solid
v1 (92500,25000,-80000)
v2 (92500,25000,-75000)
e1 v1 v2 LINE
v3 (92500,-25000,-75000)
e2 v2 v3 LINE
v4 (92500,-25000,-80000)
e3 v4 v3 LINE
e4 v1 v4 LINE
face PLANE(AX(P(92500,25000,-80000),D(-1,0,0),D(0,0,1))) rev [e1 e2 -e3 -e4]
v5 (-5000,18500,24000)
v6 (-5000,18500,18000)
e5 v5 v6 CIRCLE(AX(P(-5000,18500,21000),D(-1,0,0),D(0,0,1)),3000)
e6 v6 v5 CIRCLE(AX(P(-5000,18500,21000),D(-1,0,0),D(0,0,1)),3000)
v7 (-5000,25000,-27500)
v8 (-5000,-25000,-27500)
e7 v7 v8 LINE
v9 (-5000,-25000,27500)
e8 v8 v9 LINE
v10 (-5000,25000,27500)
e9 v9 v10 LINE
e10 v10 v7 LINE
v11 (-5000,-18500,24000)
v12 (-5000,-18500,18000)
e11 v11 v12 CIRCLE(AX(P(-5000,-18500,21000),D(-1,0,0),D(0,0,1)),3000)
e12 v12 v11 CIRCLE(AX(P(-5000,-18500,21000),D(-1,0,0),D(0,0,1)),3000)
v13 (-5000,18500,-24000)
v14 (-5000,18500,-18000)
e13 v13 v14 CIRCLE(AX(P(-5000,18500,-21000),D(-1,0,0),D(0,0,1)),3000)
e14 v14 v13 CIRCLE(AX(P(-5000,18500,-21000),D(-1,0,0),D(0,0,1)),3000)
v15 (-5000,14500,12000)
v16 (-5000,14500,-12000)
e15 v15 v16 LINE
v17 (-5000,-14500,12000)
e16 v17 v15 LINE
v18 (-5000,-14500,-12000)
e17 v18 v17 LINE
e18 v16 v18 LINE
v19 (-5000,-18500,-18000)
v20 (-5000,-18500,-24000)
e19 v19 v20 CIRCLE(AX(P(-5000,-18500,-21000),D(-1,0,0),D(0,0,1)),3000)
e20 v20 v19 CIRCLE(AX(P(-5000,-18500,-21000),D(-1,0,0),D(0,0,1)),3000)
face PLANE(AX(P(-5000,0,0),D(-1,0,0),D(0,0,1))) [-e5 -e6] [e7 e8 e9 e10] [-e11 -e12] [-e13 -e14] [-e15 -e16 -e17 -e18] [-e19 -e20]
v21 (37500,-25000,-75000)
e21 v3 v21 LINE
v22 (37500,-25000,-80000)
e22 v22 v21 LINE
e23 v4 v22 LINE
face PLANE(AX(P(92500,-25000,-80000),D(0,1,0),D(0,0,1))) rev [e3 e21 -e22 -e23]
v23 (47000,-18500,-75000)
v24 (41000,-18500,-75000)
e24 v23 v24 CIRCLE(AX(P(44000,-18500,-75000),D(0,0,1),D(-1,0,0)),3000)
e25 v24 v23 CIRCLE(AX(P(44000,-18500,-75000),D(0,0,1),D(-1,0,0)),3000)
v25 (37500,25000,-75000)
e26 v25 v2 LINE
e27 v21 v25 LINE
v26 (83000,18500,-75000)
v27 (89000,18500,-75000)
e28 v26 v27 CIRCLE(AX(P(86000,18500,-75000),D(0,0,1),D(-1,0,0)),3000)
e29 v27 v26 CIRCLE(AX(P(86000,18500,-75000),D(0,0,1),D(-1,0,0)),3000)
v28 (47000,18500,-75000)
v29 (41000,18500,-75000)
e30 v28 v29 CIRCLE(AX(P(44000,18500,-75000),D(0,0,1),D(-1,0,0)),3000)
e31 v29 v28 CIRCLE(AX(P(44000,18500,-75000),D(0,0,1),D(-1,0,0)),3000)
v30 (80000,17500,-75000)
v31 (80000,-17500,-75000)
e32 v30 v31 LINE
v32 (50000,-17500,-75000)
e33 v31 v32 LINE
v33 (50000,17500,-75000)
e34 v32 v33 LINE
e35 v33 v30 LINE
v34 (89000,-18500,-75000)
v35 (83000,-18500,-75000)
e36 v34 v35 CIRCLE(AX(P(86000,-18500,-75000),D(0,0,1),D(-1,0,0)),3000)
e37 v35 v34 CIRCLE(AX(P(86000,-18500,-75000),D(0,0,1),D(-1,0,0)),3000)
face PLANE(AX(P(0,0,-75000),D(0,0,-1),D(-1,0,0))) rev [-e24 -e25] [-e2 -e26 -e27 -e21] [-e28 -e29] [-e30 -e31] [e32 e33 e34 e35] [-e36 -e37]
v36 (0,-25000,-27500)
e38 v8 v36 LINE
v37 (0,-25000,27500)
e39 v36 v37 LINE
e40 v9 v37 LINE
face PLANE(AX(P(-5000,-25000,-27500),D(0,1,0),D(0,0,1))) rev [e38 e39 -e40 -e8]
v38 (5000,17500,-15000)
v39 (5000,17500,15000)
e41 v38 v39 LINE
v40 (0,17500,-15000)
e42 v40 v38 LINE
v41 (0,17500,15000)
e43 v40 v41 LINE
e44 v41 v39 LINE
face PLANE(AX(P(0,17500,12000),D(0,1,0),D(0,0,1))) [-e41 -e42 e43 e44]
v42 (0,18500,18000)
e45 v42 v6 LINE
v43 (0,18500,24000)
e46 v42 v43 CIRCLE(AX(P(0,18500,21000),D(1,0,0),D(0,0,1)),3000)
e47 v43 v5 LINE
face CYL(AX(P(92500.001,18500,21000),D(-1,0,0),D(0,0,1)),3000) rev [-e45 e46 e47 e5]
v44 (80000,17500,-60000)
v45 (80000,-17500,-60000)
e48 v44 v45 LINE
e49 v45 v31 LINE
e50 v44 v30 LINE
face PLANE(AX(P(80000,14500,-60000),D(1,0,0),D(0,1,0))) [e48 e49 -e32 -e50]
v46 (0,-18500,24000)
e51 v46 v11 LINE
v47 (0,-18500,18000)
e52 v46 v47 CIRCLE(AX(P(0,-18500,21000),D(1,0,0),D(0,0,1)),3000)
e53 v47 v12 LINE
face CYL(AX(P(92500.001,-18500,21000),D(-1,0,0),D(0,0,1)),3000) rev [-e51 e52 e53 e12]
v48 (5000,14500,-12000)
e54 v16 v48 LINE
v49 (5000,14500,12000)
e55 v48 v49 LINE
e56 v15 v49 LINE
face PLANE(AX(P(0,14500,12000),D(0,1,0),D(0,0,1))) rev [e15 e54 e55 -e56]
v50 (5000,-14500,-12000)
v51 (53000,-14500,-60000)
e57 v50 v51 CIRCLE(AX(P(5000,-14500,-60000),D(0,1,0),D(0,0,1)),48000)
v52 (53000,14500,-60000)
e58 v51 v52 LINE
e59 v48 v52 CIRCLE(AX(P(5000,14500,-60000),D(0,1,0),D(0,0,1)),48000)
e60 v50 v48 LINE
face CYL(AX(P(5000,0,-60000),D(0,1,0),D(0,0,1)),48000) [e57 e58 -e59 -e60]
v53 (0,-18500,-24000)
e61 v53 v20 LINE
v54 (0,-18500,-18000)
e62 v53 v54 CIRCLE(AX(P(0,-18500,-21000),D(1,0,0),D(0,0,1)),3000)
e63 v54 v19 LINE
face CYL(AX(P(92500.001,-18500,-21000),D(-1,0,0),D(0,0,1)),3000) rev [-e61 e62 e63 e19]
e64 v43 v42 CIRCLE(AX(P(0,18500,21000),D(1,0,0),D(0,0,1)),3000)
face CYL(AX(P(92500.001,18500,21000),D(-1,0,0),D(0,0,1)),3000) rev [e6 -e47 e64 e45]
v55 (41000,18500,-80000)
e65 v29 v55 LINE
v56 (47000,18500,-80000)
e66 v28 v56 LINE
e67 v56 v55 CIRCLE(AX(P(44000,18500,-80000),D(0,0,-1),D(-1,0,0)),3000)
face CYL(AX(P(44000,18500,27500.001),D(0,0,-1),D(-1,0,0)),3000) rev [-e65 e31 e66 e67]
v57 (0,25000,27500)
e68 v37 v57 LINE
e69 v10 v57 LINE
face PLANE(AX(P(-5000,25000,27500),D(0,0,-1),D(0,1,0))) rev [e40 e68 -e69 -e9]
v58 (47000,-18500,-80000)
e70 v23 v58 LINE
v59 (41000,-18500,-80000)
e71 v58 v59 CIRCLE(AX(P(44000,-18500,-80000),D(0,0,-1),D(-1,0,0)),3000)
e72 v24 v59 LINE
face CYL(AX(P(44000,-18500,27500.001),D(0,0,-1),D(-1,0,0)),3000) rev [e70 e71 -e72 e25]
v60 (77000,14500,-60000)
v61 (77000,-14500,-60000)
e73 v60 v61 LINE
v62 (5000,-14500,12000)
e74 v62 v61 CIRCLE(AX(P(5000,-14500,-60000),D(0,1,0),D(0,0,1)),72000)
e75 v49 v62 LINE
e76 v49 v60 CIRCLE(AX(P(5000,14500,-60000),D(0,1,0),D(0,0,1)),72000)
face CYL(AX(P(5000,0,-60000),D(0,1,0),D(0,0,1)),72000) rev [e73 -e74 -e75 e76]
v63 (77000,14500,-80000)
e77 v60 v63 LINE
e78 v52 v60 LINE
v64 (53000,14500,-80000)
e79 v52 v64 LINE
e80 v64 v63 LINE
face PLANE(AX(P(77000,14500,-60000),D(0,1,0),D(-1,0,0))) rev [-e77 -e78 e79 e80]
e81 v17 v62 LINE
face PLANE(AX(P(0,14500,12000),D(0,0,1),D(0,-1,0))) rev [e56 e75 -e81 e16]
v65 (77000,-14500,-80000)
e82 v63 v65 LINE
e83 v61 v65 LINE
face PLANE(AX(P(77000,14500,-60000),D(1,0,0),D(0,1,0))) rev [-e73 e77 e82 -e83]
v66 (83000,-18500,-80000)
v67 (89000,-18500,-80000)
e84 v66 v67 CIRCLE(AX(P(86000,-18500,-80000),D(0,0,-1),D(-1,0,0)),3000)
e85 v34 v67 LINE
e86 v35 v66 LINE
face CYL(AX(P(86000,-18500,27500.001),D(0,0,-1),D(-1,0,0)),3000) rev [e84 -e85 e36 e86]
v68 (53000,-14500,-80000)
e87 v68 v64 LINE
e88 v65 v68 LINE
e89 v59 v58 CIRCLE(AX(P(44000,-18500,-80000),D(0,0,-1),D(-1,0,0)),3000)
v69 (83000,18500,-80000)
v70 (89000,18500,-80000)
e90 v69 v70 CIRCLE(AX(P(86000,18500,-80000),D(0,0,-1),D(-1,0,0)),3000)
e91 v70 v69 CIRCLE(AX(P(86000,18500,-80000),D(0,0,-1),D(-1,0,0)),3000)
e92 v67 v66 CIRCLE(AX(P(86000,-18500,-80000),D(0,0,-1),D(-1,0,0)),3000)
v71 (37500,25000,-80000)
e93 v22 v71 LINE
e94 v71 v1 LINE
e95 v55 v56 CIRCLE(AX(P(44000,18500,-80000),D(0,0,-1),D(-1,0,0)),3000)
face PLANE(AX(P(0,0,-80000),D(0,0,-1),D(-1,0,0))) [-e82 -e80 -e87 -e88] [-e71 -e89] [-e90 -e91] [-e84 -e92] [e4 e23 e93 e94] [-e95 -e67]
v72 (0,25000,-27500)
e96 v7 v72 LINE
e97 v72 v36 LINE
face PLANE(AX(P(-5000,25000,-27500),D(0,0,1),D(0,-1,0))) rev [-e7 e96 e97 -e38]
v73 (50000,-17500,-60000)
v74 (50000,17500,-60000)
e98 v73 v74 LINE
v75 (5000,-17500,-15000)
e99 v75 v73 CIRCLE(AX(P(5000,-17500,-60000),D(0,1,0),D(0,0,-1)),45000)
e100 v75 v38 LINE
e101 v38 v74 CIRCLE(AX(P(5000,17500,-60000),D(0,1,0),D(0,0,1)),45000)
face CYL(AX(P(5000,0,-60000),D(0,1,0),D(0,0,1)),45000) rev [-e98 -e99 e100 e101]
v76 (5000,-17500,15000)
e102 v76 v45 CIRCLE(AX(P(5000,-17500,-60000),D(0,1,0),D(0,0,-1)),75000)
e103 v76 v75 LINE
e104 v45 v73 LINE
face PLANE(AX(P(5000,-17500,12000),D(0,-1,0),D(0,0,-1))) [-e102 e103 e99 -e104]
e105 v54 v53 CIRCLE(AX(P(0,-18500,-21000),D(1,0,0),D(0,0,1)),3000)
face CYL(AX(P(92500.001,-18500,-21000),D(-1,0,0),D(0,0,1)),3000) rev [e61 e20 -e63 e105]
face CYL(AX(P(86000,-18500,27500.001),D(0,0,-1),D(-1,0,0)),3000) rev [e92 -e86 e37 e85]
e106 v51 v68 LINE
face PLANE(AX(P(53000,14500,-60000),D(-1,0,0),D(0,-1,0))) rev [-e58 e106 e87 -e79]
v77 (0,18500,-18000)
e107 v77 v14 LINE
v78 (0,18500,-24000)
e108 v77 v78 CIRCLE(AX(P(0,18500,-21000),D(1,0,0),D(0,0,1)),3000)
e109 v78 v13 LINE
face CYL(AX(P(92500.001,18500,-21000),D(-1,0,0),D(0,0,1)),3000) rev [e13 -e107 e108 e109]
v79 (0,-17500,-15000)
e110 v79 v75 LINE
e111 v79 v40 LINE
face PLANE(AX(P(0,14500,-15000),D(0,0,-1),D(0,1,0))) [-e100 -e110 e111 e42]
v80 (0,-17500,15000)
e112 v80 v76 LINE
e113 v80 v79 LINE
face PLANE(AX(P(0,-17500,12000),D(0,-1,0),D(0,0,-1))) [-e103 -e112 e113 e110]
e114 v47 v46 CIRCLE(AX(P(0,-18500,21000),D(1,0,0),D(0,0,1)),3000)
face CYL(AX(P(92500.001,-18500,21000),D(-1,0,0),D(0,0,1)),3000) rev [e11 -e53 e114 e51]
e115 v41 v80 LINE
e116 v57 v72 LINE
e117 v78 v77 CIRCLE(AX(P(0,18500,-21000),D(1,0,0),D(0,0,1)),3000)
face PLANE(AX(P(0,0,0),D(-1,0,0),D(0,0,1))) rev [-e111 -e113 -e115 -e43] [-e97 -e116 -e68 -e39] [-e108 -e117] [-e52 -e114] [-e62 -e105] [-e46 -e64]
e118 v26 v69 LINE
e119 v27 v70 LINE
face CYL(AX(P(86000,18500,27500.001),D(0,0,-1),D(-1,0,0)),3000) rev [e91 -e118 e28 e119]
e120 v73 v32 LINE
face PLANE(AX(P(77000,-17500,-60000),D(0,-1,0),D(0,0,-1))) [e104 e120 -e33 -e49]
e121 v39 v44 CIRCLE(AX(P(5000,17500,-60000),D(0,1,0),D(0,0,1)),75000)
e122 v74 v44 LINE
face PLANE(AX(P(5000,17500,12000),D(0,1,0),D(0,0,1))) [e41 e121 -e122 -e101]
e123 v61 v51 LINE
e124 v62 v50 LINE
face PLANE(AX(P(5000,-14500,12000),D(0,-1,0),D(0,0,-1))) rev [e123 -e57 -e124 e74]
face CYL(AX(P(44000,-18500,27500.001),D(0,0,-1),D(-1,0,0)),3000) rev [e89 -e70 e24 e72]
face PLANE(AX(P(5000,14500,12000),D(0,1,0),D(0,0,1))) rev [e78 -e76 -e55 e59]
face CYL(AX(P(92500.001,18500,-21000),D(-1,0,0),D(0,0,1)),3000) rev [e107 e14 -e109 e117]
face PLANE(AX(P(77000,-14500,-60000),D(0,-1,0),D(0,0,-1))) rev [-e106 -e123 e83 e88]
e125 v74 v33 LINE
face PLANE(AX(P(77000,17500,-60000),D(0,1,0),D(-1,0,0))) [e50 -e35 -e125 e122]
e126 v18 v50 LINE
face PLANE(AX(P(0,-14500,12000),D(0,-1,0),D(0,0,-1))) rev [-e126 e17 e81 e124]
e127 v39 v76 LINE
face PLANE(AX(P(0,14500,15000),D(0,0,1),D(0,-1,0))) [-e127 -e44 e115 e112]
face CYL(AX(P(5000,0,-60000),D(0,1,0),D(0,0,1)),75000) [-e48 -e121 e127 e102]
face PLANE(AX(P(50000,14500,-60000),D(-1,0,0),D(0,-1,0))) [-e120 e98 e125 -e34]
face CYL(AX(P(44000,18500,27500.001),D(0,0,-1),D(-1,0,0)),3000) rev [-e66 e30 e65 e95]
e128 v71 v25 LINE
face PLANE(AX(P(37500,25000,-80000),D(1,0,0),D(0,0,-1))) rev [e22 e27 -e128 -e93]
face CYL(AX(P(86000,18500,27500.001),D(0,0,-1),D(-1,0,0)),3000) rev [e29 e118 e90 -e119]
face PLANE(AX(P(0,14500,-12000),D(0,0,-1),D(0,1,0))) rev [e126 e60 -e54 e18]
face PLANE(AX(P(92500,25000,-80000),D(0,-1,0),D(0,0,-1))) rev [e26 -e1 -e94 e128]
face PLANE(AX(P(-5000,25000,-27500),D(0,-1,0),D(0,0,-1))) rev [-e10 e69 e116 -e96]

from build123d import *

# Parameters (mm, degrees)
DUCT_PROFILE_SKETCH_W        = 30000
DUCT_PROFILE_SKETCH_H        = 35000
DUCT_PROFILE_SKETCH_W_2      = 24000
DUCT_PROFILE_SKETCH_H_2      = 29000
FLANGE_A_SKETCH_W            = 55000
FLANGE_A_SKETCH_H            = 50000
FLANGE_A_SKETCH_W_2          = 24000
FLANGE_A_SKETCH_H_2          = 29000
FLANGE_A_DEPTH               = 5000
FLANGE_B_SKETCH_W            = 55000
FLANGE_B_SKETCH_H            = 50000
FLANGE_B_SKETCH_W_2          = 24000
FLANGE_B_SKETCH_H_2          = 29000
FLANGE_B_DEPTH               = 5000
FLANGE_B_BOLT_HOLES_4X_REACH = 144007.208
FLANGE_B_BOLT_HOLES_SKETCH_R = 3000
FLANGE_A_BOLT_HOLES_4X_REACH = 128575.909
FLANGE_A_BOLT_HOLES_SKETCH_R = 3000


with BuildPart() as part:
    # Duct Elbow Thin Sweep: sweep along a path in Elbow Path Sketch
    with BuildLine(Plane(origin=(0, 0, 0), x_dir=(1, 0, 0), z_dir=(0, 1, 0))) as duct_elbow_thin_sweep_path:
        Line((0, 0), (5000, 0))
        ThreePointArc((5000, 0), (47426.406871193, 17573.593128807), (65000, 60000))
        Line((65000, 60000), (65000, 75000))
    # Duct Profile Sketch → Duct Elbow Thin Sweep (sweep)
    with BuildSketch(Plane(origin=(0, 0, 0), x_dir=(0, 0, -1), z_dir=(1, 0, 0))):
        Rectangle(DUCT_PROFILE_SKETCH_W, DUCT_PROFILE_SKETCH_H)
        Rectangle(DUCT_PROFILE_SKETCH_W_2, DUCT_PROFILE_SKETCH_H_2, mode=Mode.SUBTRACT)
    sweep(path=duct_elbow_thin_sweep_path.line)

    # Flange A Sketch → Flange A (add)
    with BuildSketch(Plane.ZY):
        Rectangle(FLANGE_A_SKETCH_W, FLANGE_A_SKETCH_H)
        Rectangle(FLANGE_A_SKETCH_W_2, FLANGE_A_SKETCH_H_2, mode=Mode.SUBTRACT)
    extrude(amount=FLANGE_A_DEPTH)

    # Flange B Sketch → Flange B (add)
    with BuildSketch(Plane(origin=(0, 0, -75000), x_dir=(-1, 0, 0), z_dir=(0, 0, -1))):
        with Locations((-65000, 0)):
            Rectangle(FLANGE_B_SKETCH_W, FLANGE_B_SKETCH_H)
        with Locations((-65000, 0)):
            Rectangle(FLANGE_B_SKETCH_W_2, FLANGE_B_SKETCH_H_2, mode=Mode.SUBTRACT)
    extrude(amount=FLANGE_B_DEPTH)

    # Flange B Bolt Holes Sketch → Flange B Bolt Holes 4x (cut, up to next)
    with BuildSketch(Plane(origin=(0, 0, -80000), x_dir=(-1, 0, 0), z_dir=(0, 0, -1)), mode=Mode.PRIVATE) as flange_b_bolt_holes_4x_sk1:
        with Locations((-86000, 18500)):
            Circle(FLANGE_B_BOLT_HOLES_SKETCH_R)
    flange_b_bolt_holes_4x_tool1 = extrude(flange_b_bolt_holes_4x_sk1.sketch, amount=-FLANGE_B_BOLT_HOLES_4X_REACH, mode=Mode.PRIVATE) & part.part
    # Flange B Bolt Holes Sketch → Flange B Bolt Holes 4x (cut, up to next)
    with BuildSketch(Plane(origin=(0, 0, -80000), x_dir=(-1, 0, 0), z_dir=(0, 0, -1)), mode=Mode.PRIVATE) as flange_b_bolt_holes_4x_sk2:
        with Locations((-44000, 18500)):
            Circle(FLANGE_B_BOLT_HOLES_SKETCH_R)
    flange_b_bolt_holes_4x_tool2 = extrude(flange_b_bolt_holes_4x_sk2.sketch, amount=-FLANGE_B_BOLT_HOLES_4X_REACH, mode=Mode.PRIVATE) & part.part
    # Flange B Bolt Holes Sketch → Flange B Bolt Holes 4x (cut, up to next)
    with BuildSketch(Plane(origin=(0, 0, -80000), x_dir=(-1, 0, 0), z_dir=(0, 0, -1)), mode=Mode.PRIVATE) as flange_b_bolt_holes_4x_sk3:
        with Locations((-44000, -18500)):
            Circle(FLANGE_B_BOLT_HOLES_SKETCH_R)
    flange_b_bolt_holes_4x_tool3 = extrude(flange_b_bolt_holes_4x_sk3.sketch, amount=-FLANGE_B_BOLT_HOLES_4X_REACH, mode=Mode.PRIVATE) & part.part
    # Flange B Bolt Holes Sketch → Flange B Bolt Holes 4x (cut, up to next)
    with BuildSketch(Plane(origin=(0, 0, -80000), x_dir=(-1, 0, 0), z_dir=(0, 0, -1)), mode=Mode.PRIVATE) as flange_b_bolt_holes_4x_sk4:
        with Locations((-86000, -18500)):
            Circle(FLANGE_B_BOLT_HOLES_SKETCH_R)
    flange_b_bolt_holes_4x_tool4 = extrude(flange_b_bolt_holes_4x_sk4.sketch, amount=-FLANGE_B_BOLT_HOLES_4X_REACH, mode=Mode.PRIVATE) & part.part
    add(flange_b_bolt_holes_4x_tool1.solids().sort_by_distance((86000, 18500, -80000))[0], mode=Mode.SUBTRACT)
    add(flange_b_bolt_holes_4x_tool2.solids().sort_by_distance((44000, 18500, -80000))[0], mode=Mode.SUBTRACT)
    add(flange_b_bolt_holes_4x_tool3.solids().sort_by_distance((44000, -18500, -80000))[0], mode=Mode.SUBTRACT)
    add(flange_b_bolt_holes_4x_tool4.solids().sort_by_distance((86000, -18500, -80000))[0], mode=Mode.SUBTRACT)

    # Flange A Bolt Holes Sketch → Flange A Bolt Holes 4x (cut, up to next)
    with BuildSketch(Plane.ZY.offset(5000), mode=Mode.PRIVATE) as flange_a_bolt_holes_4x_sk1:
        with Locations((-21000, 18500)):
            Circle(FLANGE_A_BOLT_HOLES_SKETCH_R)
    flange_a_bolt_holes_4x_tool1 = extrude(flange_a_bolt_holes_4x_sk1.sketch, amount=-FLANGE_A_BOLT_HOLES_4X_REACH, mode=Mode.PRIVATE) & part.part
    # Flange A Bolt Holes Sketch → Flange A Bolt Holes 4x (cut, up to next)
    with BuildSketch(Plane.ZY.offset(5000), mode=Mode.PRIVATE) as flange_a_bolt_holes_4x_sk2:
        with Locations((21000, 18500)):
            Circle(FLANGE_A_BOLT_HOLES_SKETCH_R)
    flange_a_bolt_holes_4x_tool2 = extrude(flange_a_bolt_holes_4x_sk2.sketch, amount=-FLANGE_A_BOLT_HOLES_4X_REACH, mode=Mode.PRIVATE) & part.part
    # Flange A Bolt Holes Sketch → Flange A Bolt Holes 4x (cut, up to next)
    with BuildSketch(Plane.ZY.offset(5000), mode=Mode.PRIVATE) as flange_a_bolt_holes_4x_sk3:
        with Locations((21000, -18500)):
            Circle(FLANGE_A_BOLT_HOLES_SKETCH_R)
    flange_a_bolt_holes_4x_tool3 = extrude(flange_a_bolt_holes_4x_sk3.sketch, amount=-FLANGE_A_BOLT_HOLES_4X_REACH, mode=Mode.PRIVATE) & part.part
    # Flange A Bolt Holes Sketch → Flange A Bolt Holes 4x (cut, up to next)
    with BuildSketch(Plane.ZY.offset(5000), mode=Mode.PRIVATE) as flange_a_bolt_holes_4x_sk4:
        with Locations((-21000, -18500)):
            Circle(FLANGE_A_BOLT_HOLES_SKETCH_R)
    flange_a_bolt_holes_4x_tool4 = extrude(flange_a_bolt_holes_4x_sk4.sketch, amount=-FLANGE_A_BOLT_HOLES_4X_REACH, mode=Mode.PRIVATE) & part.part
    add(flange_a_bolt_holes_4x_tool1.solids().sort_by_distance((-5000, 18500, -21000))[0], mode=Mode.SUBTRACT)
    add(flange_a_bolt_holes_4x_tool2.solids().sort_by_distance((-5000, 18500, 21000))[0], mode=Mode.SUBTRACT)
    add(flange_a_bolt_holes_4x_tool3.solids().sort_by_distance((-5000, -18500, 21000))[0], mode=Mode.SUBTRACT)
    add(flange_a_bolt_holes_4x_tool4.solids().sort_by_distance((-5000, -18500, -21000))[0], mode=Mode.SUBTRACT)


solid = part.part
